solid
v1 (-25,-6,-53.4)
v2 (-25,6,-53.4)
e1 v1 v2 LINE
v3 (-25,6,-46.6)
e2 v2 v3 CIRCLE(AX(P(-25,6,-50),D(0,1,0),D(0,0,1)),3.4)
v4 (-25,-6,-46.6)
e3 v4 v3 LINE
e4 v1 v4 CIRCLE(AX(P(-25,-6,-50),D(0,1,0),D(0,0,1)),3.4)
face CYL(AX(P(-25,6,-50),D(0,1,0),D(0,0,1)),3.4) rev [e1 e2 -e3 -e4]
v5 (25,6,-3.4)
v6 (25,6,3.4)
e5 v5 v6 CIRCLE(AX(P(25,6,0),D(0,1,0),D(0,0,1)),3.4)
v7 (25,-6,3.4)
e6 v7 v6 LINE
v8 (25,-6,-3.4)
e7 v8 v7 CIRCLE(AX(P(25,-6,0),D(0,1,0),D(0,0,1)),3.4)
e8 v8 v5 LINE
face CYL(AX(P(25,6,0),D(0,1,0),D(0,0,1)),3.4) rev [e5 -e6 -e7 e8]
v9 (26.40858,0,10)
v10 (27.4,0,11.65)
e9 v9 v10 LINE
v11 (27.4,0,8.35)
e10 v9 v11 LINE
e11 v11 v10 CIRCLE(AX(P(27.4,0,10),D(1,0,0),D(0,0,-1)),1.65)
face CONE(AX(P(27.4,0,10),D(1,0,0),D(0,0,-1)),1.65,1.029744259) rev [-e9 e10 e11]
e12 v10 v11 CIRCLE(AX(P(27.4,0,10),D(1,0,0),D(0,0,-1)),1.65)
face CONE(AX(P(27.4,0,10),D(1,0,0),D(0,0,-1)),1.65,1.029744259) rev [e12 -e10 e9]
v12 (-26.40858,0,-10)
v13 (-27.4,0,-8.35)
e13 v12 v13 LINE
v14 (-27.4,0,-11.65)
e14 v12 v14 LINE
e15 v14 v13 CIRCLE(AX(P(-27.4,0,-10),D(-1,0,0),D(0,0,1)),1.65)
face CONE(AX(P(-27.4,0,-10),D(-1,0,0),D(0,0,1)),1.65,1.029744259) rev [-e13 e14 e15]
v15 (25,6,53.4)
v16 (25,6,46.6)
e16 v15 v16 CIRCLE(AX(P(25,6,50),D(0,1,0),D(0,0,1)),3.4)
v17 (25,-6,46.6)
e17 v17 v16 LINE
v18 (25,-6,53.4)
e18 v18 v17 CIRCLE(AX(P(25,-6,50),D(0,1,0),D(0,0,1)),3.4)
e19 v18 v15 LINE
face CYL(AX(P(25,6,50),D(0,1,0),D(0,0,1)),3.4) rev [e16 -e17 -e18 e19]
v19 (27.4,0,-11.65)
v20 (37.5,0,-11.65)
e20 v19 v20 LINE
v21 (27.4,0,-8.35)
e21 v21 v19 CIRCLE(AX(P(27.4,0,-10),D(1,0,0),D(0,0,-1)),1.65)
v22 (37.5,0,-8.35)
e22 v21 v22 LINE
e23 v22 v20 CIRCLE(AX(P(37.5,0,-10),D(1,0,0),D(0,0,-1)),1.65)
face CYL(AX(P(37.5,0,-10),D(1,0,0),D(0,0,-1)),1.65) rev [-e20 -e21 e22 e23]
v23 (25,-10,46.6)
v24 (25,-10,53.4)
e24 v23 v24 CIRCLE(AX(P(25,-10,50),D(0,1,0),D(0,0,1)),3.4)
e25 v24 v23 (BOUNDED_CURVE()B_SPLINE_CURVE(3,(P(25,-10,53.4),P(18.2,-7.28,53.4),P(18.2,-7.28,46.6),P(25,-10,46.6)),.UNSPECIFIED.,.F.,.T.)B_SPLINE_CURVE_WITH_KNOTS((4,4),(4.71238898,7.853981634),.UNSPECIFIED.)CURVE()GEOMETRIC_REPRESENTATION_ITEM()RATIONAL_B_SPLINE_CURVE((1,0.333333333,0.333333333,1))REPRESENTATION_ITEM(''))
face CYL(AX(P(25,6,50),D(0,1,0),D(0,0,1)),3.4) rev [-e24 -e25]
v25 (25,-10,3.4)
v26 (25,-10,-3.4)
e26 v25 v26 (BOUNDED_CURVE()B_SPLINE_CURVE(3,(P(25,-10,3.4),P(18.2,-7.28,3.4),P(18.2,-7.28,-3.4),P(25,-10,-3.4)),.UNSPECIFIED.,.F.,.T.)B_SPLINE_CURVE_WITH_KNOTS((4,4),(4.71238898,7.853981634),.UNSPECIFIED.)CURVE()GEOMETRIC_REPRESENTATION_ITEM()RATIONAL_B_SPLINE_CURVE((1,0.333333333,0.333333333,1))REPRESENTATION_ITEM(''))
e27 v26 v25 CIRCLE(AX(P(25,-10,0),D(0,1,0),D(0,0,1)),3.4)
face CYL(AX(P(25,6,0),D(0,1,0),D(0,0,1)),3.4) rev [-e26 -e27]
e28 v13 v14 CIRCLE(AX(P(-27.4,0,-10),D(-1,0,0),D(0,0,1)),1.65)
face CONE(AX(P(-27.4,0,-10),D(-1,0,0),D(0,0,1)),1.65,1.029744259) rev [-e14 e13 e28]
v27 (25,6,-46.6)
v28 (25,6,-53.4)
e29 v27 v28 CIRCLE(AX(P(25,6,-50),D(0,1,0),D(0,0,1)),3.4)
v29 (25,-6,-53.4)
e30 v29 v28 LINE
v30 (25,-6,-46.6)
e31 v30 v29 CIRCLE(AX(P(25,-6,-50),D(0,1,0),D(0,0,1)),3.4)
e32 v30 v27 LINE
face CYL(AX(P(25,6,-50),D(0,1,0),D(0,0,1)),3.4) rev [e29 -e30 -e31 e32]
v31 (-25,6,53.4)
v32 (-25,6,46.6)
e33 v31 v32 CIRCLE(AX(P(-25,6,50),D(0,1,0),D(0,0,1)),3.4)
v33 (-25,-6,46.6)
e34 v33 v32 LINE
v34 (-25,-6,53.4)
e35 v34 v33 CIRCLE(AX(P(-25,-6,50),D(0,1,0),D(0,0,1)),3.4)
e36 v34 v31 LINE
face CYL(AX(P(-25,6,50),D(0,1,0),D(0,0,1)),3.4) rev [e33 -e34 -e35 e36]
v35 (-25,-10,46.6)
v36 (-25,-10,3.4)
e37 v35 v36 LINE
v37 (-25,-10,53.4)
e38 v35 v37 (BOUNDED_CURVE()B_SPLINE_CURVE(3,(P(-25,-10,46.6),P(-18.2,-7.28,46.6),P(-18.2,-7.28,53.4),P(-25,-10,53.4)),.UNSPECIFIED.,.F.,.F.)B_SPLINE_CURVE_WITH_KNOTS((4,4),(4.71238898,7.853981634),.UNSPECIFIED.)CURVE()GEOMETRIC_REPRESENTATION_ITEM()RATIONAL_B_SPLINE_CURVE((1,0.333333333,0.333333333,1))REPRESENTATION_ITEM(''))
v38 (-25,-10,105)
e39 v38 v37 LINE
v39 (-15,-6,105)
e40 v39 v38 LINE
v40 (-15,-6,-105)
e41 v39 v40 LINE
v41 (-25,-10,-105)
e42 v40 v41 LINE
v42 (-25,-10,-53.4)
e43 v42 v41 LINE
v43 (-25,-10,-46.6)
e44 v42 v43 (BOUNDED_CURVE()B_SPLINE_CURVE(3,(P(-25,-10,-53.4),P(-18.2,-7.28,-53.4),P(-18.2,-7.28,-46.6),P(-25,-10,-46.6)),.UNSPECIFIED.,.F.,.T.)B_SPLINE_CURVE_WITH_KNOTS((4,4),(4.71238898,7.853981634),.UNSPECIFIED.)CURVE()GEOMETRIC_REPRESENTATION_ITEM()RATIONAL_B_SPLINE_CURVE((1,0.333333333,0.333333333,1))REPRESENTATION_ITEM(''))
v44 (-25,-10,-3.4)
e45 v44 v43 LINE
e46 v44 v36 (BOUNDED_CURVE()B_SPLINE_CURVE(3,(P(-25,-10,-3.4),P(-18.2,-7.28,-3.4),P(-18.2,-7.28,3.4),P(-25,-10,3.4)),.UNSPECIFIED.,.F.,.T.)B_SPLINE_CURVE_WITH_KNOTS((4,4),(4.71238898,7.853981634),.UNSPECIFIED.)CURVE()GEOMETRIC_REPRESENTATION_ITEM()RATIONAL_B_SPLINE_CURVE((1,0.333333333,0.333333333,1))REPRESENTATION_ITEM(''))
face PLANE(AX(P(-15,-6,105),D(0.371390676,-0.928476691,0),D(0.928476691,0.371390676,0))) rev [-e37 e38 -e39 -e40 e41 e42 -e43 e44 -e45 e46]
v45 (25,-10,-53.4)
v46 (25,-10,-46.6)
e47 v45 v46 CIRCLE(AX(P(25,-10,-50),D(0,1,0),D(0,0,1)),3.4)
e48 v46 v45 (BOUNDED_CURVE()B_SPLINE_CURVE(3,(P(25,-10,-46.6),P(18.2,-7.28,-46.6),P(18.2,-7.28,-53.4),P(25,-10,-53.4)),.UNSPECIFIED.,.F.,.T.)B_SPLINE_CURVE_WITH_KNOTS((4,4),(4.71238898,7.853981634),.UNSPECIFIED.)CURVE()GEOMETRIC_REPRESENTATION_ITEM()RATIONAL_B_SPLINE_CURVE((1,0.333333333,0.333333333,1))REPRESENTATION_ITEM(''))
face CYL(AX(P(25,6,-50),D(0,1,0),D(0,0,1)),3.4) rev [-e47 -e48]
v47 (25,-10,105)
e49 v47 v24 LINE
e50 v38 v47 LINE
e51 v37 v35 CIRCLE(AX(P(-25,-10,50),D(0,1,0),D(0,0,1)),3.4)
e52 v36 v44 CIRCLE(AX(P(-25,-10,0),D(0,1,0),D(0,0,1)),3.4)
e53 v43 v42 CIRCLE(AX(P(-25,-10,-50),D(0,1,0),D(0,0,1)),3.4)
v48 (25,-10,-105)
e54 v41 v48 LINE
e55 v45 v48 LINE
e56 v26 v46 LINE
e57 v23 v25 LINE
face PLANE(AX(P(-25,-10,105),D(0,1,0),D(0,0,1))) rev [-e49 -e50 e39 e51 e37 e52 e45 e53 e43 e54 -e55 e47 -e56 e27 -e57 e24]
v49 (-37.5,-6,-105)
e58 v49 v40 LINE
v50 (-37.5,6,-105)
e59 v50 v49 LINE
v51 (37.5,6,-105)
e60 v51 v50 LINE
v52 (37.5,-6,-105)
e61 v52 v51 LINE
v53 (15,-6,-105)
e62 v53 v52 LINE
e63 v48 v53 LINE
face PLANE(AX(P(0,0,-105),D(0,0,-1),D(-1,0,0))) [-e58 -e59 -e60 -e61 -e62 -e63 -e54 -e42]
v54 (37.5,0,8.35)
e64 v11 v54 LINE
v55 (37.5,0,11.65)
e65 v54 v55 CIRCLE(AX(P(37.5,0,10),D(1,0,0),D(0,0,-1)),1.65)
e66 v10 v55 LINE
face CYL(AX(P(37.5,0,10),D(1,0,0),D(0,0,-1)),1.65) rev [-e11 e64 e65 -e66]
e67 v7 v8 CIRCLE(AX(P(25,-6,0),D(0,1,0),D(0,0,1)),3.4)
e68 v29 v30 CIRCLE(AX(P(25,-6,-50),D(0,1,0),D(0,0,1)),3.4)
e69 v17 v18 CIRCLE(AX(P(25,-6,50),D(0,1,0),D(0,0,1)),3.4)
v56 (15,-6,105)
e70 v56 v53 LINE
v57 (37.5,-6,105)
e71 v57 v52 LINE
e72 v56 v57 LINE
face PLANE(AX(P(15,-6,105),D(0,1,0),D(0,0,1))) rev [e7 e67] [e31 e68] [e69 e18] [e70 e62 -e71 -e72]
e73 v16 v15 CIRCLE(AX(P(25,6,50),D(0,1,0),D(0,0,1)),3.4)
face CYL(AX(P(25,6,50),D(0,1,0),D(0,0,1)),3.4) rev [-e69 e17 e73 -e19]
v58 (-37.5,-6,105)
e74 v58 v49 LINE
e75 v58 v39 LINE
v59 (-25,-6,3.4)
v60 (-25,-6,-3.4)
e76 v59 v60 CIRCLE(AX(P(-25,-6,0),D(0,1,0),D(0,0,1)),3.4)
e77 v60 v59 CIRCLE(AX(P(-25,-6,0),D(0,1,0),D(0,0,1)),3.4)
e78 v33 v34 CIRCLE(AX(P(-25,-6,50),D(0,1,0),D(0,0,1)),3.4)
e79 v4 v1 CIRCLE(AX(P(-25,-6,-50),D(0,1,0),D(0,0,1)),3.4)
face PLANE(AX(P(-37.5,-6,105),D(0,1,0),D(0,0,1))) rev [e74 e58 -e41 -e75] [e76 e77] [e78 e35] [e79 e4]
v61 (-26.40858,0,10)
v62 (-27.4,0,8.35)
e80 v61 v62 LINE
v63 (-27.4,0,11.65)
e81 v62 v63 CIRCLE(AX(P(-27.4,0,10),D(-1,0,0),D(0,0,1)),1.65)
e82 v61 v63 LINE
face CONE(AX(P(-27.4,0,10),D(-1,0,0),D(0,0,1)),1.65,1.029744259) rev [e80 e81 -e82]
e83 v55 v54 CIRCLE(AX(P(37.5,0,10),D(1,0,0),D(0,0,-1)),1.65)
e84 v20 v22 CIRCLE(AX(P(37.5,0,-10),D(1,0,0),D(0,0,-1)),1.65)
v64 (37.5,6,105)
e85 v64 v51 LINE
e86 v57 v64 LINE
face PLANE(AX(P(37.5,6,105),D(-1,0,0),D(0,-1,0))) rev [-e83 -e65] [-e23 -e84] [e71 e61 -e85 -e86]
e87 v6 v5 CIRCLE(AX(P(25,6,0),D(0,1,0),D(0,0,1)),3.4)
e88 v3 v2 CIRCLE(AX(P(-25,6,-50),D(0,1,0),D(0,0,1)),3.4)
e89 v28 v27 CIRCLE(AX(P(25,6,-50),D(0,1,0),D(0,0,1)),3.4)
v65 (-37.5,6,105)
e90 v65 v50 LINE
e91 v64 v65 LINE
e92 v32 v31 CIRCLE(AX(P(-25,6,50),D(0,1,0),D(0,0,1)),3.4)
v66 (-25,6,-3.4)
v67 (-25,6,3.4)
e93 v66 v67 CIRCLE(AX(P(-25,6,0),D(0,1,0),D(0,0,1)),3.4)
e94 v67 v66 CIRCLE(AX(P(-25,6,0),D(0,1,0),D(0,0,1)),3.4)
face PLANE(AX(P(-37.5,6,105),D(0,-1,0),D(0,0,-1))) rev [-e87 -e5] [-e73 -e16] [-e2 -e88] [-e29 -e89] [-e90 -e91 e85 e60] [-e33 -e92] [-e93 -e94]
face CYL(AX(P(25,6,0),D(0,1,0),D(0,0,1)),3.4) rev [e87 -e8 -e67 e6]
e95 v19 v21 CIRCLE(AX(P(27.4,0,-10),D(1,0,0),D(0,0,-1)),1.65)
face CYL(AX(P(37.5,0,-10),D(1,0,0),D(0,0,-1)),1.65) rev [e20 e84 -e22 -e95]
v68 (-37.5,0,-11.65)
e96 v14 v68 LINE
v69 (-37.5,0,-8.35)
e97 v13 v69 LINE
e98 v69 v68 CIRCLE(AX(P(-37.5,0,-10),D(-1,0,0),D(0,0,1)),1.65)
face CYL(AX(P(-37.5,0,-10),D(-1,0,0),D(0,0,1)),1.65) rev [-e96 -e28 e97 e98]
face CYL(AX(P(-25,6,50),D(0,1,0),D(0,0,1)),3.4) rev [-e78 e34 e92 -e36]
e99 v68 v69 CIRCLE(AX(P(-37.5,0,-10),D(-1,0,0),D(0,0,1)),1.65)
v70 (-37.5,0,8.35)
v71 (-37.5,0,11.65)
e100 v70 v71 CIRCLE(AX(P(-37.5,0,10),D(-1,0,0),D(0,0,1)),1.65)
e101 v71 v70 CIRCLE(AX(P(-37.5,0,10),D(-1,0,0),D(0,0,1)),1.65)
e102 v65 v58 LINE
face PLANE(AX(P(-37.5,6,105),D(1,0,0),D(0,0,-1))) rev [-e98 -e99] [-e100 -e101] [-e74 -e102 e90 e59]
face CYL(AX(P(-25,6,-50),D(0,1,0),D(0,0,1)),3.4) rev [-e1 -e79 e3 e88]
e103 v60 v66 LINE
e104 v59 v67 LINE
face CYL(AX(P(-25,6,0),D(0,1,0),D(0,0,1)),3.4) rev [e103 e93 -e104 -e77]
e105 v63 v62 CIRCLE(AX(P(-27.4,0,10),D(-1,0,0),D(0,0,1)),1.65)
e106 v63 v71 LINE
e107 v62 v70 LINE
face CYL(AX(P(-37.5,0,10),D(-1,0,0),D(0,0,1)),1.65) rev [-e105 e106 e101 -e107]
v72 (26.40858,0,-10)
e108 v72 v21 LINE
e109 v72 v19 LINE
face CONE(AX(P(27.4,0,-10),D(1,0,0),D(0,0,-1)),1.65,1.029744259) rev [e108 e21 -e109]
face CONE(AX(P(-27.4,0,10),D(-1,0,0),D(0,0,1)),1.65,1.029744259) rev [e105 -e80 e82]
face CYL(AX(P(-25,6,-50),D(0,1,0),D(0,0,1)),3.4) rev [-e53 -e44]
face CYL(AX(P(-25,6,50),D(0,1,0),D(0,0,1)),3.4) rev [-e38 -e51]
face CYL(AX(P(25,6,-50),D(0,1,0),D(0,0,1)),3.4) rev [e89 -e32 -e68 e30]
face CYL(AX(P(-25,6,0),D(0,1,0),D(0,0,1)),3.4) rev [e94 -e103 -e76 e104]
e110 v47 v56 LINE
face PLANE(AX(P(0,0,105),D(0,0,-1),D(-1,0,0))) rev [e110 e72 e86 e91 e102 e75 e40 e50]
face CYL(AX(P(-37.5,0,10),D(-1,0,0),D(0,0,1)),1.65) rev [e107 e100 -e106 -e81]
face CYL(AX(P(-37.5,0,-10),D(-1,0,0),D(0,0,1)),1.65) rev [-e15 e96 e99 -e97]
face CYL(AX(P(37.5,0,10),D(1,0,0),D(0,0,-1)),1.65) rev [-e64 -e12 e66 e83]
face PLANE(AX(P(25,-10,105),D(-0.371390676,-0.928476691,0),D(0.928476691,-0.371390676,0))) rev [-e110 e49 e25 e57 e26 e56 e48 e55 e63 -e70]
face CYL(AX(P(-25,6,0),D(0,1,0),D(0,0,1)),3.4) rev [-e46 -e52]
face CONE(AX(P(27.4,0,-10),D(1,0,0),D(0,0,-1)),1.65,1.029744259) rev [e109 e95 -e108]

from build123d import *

# Parameters (mm, degrees)
EXTRUDE_1_DEPTH             = 105
HOLE_WIZARD_M4_1_AT_2_COUNT = 2
HOLE_WIZARD_M4_1_AT_2_PITCH = 20
PATTERN_LINEAR_1_COUNT      = 3
PATTERN_LINEAR_1_PITCH      = 50
PATTERN_LINEAR_1_COUNT_DIR2 = 2
PATTERN_LINEAR_1_PITCH_DIR2 = 50


with BuildPart() as part:
    # 草图1 → 凸台-拉伸1 (new, symmetric)
    with BuildSketch(Plane.XY):
        Polygon((-25, -10), (25, -10), (15, -6), (37.5, -6), (37.5, 6), (-37.5, 6), (-37.5, -6), (-15, -6), align=None)
    extrude(amount=EXTRUDE_1_DEPTH, both=True)

    # 草图2 → M4 螺纹孔1 (revolve, cut)
    with BuildSketch(Plane(origin=(-37.5, 0, -10), x_dir=(0, 0, 1), z_dir=(0, 1, 0))):
        Polygon((0, 0), (0, 11.091420021), (1.65, 10.1), (1.65, 0), align=None)
    hole_wizard_m4_1 = revolve(axis=Axis((-43.85, 0, -10), (1, 0, 0)), mode=Mode.SUBTRACT)

    # M4 螺纹孔1 at 2: M4 螺纹孔1 ×2
    with Locations(*[(0, 0, i * HOLE_WIZARD_M4_1_AT_2_PITCH) for i in range(1, HOLE_WIZARD_M4_1_AT_2_COUNT)]):
        add(hole_wizard_m4_1, mode=Mode.SUBTRACT)

    # 镜向1: M4 螺纹孔1 across plane
    add(hole_wizard_m4_1.mirror(Plane(origin=(0, 0, 0), x_dir=(0, 0, 1), z_dir=(1, 0, 0))), mode=Mode.SUBTRACT)

    # 镜向1 copy 1 sketch → 镜向1 copy 1 (revolve, cut)
    with BuildSketch(Plane(origin=(37.5, 0, 10), x_dir=(0, 0, 1), z_dir=(0, 1, 0))):
        Polygon((0, 0), (0, -11.091420021), (1.65, -10.1), (1.65, 0), align=None)
    revolve(axis=Axis((43.85, 0, 10), (1, 0, 0)), mode=Mode.SUBTRACT)

    # 草图4 → M8 螺纹孔1 (revolve, cut)
    with BuildSketch(Plane(origin=(-25, 6, -50), x_dir=(0, 0, 1), z_dir=(1, 0, 0))):
        Polygon((0, 0), (0, 21.792926105), (3.4, 19.75), (3.4, 0), align=None)
    hole_wizard_m8_1 = revolve(axis=Axis((-25, 12.35, -50), (0, -1, 0)), mode=Mode.SUBTRACT)

    # 阵列(线性)1: Hole Wizard M8 _1 3 × 2
    with Locations(*[(j * PATTERN_LINEAR_1_PITCH_DIR2, 0, i * PATTERN_LINEAR_1_PITCH) for i in range(PATTERN_LINEAR_1_COUNT) for j in range(PATTERN_LINEAR_1_COUNT_DIR2) if (i, j) != (0, 0)]):
        add(hole_wizard_m8_1, mode=Mode.SUBTRACT)


solid = part.part
